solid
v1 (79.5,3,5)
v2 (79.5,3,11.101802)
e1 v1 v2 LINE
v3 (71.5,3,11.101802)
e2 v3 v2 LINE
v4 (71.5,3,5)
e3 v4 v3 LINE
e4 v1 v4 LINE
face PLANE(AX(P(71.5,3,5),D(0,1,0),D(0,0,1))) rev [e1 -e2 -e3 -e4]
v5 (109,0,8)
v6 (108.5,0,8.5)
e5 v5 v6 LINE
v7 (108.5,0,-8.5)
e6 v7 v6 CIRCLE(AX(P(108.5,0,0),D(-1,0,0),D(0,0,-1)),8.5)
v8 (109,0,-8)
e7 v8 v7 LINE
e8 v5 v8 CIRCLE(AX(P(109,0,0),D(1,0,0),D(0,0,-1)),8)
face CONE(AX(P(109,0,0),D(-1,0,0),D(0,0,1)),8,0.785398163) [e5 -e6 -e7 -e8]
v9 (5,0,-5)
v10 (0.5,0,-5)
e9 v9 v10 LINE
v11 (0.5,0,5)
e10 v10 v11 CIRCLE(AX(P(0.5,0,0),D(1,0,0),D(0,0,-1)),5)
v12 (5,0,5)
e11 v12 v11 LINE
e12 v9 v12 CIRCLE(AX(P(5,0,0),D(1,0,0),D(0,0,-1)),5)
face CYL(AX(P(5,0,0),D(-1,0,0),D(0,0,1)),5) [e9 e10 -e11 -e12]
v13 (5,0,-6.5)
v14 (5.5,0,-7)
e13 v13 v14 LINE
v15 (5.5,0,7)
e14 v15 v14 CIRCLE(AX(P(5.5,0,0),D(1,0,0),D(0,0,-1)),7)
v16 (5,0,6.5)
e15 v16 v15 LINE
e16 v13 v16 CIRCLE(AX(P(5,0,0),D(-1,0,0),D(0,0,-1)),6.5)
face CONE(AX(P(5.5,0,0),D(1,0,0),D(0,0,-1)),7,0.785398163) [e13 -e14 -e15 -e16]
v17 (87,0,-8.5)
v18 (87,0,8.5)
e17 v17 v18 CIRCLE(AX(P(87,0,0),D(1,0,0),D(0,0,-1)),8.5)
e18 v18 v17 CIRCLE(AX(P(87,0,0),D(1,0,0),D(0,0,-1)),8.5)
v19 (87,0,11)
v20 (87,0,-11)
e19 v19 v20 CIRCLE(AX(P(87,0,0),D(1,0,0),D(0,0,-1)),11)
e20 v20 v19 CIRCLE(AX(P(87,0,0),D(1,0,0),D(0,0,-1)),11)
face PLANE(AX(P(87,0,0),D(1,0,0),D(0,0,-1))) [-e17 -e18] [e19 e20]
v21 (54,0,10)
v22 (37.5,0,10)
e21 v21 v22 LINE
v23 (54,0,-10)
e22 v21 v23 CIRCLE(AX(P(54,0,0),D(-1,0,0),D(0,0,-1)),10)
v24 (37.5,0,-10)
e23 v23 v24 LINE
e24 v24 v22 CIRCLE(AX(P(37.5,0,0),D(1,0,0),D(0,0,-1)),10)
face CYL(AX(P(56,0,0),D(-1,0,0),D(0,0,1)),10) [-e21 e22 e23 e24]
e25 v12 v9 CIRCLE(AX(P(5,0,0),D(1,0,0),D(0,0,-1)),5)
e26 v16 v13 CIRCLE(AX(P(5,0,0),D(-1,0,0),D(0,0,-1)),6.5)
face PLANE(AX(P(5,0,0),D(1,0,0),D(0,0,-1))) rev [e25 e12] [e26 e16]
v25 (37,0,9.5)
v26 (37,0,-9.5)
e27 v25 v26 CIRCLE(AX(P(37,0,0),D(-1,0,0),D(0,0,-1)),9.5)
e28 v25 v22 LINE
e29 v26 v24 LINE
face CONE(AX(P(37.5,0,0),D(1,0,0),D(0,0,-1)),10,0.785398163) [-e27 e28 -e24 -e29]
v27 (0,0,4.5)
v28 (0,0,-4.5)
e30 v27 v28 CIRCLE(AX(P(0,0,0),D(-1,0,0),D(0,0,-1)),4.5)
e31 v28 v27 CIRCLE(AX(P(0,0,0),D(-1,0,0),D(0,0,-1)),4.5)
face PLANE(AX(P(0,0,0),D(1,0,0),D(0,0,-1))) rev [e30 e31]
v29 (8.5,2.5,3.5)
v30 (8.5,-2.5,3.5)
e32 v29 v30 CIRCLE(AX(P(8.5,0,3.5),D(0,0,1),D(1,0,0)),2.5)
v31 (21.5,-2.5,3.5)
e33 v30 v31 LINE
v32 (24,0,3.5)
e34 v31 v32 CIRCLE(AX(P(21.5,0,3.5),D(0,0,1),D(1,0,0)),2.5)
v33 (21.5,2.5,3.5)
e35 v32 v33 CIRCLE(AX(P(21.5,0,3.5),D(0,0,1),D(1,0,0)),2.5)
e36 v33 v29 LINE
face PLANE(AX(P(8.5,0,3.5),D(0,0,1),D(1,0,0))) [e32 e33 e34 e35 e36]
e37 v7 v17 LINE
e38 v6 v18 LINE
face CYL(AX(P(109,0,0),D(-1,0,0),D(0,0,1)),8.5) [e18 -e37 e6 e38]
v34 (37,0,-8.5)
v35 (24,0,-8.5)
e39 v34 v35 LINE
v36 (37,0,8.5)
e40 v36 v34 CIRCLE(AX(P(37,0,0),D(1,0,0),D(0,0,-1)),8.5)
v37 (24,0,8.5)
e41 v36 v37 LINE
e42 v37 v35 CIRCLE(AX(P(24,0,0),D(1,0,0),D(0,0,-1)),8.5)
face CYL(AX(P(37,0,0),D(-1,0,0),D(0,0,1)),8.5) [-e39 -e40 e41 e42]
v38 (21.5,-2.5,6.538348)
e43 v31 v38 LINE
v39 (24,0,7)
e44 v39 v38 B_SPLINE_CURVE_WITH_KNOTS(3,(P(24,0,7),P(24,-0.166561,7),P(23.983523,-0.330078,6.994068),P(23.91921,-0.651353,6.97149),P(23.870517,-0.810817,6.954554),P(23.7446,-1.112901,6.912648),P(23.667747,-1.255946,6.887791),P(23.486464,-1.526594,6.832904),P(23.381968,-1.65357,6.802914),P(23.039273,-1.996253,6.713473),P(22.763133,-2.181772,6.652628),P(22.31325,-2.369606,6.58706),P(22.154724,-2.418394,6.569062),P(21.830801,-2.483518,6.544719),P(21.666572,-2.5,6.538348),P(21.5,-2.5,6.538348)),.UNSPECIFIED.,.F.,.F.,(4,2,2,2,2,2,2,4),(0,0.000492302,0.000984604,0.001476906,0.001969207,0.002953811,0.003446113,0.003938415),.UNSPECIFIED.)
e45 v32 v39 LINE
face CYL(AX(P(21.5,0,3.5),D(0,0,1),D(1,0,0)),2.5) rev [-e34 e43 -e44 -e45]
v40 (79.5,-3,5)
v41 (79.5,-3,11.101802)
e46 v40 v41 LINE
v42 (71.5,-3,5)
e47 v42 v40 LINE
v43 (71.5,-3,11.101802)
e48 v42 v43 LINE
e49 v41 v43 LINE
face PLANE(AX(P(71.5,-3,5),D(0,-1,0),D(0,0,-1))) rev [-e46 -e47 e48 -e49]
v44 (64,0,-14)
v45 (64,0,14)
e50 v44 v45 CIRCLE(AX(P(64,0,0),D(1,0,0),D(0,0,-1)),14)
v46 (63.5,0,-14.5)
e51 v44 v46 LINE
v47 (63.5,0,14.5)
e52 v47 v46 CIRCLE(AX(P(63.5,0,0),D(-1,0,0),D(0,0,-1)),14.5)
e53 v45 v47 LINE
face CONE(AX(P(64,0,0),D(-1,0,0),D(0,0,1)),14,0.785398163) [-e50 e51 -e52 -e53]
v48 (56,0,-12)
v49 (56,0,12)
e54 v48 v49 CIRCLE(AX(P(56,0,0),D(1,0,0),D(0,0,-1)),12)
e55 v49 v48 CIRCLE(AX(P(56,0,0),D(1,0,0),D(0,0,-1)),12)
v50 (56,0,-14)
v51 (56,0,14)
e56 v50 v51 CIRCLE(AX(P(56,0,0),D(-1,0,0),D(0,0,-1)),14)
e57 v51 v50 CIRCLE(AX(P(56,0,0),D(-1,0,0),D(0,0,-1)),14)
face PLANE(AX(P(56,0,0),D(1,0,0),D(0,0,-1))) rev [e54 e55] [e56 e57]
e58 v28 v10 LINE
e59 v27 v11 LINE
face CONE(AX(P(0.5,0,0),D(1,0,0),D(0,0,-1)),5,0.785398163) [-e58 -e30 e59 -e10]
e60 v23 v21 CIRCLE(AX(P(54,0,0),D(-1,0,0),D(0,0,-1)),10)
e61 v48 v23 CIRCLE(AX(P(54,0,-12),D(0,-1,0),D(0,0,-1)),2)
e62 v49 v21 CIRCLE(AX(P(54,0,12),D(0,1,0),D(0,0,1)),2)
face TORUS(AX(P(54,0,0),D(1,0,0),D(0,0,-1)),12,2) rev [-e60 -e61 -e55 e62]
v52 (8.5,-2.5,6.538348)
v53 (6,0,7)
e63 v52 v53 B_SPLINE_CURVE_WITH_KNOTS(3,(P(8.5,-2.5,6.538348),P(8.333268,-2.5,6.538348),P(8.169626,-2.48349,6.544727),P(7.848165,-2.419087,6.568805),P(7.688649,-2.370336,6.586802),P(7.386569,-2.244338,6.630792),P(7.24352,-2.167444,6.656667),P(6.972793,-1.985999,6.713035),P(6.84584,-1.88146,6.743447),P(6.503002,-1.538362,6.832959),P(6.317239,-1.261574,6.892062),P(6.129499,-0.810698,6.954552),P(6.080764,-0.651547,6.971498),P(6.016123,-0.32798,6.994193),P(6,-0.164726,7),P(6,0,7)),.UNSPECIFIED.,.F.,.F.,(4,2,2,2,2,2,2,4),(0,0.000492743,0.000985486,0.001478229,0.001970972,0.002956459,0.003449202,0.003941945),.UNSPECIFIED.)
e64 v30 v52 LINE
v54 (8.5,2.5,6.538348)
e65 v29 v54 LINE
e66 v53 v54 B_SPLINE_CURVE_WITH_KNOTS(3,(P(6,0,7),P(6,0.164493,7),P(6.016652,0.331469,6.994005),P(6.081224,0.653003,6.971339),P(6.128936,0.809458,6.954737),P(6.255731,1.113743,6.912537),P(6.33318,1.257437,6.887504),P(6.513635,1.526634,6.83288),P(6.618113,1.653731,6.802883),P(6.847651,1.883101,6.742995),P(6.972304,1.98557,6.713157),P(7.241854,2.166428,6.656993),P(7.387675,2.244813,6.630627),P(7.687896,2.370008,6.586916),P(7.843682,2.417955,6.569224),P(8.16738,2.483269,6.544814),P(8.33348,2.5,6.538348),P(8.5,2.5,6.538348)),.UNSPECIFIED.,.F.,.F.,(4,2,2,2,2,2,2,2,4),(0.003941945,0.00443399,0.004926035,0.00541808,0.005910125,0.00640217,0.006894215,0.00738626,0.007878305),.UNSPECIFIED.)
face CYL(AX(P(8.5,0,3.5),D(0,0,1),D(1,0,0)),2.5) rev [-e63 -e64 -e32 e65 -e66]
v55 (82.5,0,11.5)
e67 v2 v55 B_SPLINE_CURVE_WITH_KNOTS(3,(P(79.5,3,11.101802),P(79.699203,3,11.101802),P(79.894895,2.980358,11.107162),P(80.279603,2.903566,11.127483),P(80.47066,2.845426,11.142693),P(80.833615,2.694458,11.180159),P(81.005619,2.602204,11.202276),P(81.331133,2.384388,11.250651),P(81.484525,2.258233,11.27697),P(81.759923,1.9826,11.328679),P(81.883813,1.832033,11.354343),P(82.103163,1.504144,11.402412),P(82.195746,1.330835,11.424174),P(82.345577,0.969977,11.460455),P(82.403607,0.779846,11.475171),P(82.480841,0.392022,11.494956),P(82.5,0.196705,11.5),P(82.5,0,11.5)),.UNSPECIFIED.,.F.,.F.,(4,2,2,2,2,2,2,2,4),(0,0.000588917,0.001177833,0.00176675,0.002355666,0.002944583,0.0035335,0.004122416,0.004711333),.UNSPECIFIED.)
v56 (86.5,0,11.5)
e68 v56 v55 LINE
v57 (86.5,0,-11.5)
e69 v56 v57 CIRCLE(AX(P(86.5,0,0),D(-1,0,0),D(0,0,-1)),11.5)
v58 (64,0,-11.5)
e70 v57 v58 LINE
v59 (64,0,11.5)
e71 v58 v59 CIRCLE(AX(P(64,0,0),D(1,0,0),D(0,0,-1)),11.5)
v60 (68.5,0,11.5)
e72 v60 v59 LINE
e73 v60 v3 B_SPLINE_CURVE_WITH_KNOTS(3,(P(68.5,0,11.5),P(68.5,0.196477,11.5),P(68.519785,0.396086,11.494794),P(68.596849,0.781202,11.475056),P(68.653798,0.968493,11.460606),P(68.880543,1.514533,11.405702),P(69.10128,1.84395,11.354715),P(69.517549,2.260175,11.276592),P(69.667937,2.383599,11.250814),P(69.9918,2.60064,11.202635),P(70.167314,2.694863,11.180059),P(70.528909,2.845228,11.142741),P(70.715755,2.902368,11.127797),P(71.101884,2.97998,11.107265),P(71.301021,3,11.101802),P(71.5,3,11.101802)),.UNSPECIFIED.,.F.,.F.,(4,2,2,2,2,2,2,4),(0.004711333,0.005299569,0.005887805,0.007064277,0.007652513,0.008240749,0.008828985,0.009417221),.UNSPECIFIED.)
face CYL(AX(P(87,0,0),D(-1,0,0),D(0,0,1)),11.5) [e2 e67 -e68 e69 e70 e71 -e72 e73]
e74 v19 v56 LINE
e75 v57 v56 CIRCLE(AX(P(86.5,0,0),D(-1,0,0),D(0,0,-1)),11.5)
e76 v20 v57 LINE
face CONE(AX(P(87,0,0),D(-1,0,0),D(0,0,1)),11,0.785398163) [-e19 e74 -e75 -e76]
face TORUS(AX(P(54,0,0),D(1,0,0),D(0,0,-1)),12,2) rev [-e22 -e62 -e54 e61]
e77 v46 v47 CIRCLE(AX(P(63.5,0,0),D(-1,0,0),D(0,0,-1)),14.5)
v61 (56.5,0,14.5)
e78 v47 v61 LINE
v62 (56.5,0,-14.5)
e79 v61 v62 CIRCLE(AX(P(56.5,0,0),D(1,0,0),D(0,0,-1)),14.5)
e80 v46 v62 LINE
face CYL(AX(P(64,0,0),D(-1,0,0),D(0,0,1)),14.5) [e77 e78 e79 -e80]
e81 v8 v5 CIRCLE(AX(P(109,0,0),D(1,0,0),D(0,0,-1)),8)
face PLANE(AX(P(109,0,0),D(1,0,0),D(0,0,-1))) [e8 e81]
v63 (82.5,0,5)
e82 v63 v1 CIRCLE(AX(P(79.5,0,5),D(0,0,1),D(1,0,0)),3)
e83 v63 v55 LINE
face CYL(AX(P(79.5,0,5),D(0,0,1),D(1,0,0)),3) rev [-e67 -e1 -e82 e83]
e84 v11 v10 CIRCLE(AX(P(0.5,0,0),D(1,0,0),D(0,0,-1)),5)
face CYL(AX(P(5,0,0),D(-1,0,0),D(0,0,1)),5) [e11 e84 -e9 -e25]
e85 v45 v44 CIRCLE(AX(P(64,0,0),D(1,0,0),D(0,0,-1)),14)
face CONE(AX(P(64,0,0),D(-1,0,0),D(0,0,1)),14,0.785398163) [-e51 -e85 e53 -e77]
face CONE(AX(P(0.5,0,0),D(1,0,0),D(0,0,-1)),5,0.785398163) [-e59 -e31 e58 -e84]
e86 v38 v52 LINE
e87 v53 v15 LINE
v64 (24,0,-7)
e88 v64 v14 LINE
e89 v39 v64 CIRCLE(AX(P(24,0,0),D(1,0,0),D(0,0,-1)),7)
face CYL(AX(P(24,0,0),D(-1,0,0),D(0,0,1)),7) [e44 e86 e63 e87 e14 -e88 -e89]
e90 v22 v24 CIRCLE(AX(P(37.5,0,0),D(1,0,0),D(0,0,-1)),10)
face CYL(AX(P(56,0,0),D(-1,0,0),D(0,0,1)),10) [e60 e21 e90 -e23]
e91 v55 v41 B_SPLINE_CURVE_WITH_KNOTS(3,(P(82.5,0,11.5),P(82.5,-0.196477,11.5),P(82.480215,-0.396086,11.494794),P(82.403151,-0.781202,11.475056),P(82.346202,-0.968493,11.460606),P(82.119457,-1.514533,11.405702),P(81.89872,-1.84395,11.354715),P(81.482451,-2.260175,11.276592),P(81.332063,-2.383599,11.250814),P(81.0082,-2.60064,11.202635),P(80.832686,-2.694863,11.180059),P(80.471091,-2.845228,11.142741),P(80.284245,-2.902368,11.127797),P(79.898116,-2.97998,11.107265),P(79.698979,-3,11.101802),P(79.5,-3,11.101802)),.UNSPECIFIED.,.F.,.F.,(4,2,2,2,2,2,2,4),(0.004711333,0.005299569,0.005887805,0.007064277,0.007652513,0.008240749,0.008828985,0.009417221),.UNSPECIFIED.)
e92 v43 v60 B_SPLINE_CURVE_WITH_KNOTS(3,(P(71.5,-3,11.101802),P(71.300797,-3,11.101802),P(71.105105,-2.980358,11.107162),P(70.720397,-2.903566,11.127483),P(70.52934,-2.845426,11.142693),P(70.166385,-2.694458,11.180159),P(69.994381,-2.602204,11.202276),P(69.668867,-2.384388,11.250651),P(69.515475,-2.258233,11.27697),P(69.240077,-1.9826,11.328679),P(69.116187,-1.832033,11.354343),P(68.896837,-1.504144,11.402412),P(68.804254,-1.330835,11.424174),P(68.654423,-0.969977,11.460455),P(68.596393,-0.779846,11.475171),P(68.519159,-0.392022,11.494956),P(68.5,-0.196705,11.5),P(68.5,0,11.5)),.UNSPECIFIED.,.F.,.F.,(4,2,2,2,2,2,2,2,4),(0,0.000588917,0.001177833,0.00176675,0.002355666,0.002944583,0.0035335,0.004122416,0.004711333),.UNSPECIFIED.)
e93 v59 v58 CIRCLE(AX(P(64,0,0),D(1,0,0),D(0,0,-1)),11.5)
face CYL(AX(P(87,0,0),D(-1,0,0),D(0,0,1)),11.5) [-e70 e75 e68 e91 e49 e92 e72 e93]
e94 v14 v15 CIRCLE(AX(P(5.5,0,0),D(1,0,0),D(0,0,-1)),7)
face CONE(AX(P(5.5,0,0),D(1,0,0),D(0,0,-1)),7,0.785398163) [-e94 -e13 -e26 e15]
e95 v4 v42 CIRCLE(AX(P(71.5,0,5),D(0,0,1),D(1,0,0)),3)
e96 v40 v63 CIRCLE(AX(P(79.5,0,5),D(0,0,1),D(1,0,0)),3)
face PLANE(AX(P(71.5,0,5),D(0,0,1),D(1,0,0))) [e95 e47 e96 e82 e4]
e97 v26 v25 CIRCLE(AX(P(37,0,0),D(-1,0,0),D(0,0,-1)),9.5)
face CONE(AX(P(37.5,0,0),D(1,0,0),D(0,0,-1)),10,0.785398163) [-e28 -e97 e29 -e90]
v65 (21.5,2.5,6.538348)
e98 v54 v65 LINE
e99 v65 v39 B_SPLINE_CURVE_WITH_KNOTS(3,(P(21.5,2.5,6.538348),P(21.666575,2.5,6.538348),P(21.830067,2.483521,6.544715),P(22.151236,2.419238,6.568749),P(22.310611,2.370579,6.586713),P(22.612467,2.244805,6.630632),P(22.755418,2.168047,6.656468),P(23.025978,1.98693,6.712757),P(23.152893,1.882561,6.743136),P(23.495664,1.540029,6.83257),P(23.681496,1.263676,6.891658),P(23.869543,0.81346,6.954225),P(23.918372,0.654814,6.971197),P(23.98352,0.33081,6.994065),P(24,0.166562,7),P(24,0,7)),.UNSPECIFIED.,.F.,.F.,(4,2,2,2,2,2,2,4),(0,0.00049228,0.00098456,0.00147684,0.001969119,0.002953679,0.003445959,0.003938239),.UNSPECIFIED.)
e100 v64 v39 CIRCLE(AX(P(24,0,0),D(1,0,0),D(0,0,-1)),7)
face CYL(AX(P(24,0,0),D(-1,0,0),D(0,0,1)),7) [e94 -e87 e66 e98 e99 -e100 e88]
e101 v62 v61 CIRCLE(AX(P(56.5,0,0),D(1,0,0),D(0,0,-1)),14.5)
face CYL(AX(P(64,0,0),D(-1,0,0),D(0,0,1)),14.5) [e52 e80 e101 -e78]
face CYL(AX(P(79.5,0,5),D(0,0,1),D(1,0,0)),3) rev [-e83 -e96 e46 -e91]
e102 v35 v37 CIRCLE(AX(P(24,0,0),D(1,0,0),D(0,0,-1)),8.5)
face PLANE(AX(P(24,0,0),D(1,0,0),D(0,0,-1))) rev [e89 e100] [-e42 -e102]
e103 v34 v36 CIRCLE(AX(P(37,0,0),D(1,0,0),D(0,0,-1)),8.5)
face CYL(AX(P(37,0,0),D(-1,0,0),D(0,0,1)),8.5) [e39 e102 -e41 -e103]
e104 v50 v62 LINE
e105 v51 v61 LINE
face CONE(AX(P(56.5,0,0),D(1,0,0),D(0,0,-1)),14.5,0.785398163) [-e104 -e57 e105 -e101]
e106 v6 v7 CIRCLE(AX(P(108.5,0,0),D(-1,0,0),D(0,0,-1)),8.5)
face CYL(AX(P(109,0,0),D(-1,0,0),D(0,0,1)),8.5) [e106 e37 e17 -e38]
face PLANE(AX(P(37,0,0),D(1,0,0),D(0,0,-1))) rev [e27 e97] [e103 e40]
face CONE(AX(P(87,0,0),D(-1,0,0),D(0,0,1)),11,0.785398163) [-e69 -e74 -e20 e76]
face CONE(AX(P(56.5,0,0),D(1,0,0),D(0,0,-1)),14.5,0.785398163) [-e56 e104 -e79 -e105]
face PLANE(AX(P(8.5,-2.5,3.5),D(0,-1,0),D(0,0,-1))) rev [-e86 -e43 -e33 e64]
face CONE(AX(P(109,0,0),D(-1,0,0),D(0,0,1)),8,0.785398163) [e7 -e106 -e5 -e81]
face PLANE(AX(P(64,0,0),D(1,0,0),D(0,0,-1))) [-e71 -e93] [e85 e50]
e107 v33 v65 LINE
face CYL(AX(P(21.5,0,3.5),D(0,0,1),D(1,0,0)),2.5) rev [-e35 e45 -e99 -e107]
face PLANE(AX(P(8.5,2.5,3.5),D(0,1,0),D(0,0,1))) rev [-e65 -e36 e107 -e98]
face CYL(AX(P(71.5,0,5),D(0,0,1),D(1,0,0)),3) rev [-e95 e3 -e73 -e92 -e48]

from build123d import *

# Parameters (mm, degrees)
SKETCH1_R           = 5
BOSS_EXTRUDE1_DEPTH = 5
SKETCH2_R           = 7
BOSS_EXTRUDE2_DEPTH = 19
SKETCH3_R           = 8.5
BOSS_EXTRUDE3_DEPTH = 13
SKETCH4_R           = 10
BOSS_EXTRUDE4_DEPTH = 19
SKETCH5_R           = 14.5
BOSS_EXTRUDE5_DEPTH = 8
SKETCH6_R           = 11.5
BOSS_EXTRUDE6_DEPTH = 23
SKETCH7_R           = 8.5
BOSS_EXTRUDE7_DEPTH = 22
CHAMFER1_SIZE       = 0.5
CUT_EXTRUDE2_START  = 7
CUT_EXTRUDE2_DEPTH  = 3.5
CUT_EXTRUDE3_START  = 11.5
CUT_EXTRUDE3_DEPTH  = 6.5
FILLET1_R           = 2


with BuildPart() as part:
    # Sketch1 → Boss-Extrude1 (new body)
    with BuildSketch(Plane(origin=(0, 0, 0), x_dir=(0, 0, -1), z_dir=(1, 0, 0))):
        Circle(SKETCH1_R)
    extrude(amount=BOSS_EXTRUDE1_DEPTH)

    # Sketch2 → Boss-Extrude2 (add)
    with BuildSketch(Plane(origin=(5, 0, 0), x_dir=(0, 0, -1), z_dir=(1, 0, 0))):
        Circle(SKETCH2_R)
    extrude(amount=BOSS_EXTRUDE2_DEPTH)

    # Sketch3 → Boss-Extrude3 (add)
    with BuildSketch(Plane(origin=(24, 0, 0), x_dir=(0, 0, -1), z_dir=(1, 0, 0))):
        with Locations(Location((0, 0, 0), (0, 0, 180))):
            Circle(SKETCH3_R)
    extrude(amount=BOSS_EXTRUDE3_DEPTH)

    # Sketch4 → Boss-Extrude4 (add)
    with BuildSketch(Plane(origin=(37, 0, 0), x_dir=(0, 0, -1), z_dir=(1, 0, 0))):
        Circle(SKETCH4_R)
    extrude(amount=BOSS_EXTRUDE4_DEPTH)

    # Sketch5 → Boss-Extrude5 (add)
    with BuildSketch(Plane(origin=(56, 0, 0), x_dir=(0, 0, -1), z_dir=(1, 0, 0))):
        Circle(SKETCH5_R)
    extrude(amount=BOSS_EXTRUDE5_DEPTH)

    # Sketch6 → Boss-Extrude6 (add)
    with BuildSketch(Plane(origin=(64, 0, 0), x_dir=(0, 0, -1), z_dir=(1, 0, 0))):
        Circle(SKETCH6_R)
    extrude(amount=BOSS_EXTRUDE6_DEPTH)

    # Sketch7 → Boss-Extrude7 (add)
    with BuildSketch(Plane(origin=(87, 0, 0), x_dir=(0, 0, -1), z_dir=(1, 0, 0))):
        with Locations(Location((0, 0, 0), (0, 0, 180))):
            Circle(SKETCH7_R)
    extrude(amount=BOSS_EXTRUDE7_DEPTH)

    # Chamfer1
    chamfer1_edges = [part.edges().sort_by_distance(p)[0] for p in [
        (37, 0, 10),
        (56, 0, 14.5),
        (0, 0, 5),
        (64, 0, 14.5),
        (87, 0, 11.5),
        (109, 0, -8.5),
        (5, 0, 7),
    ]]
    chamfer(chamfer1_edges, length=CHAMFER1_SIZE)

    # Sketch8 → Cut-Extrude2 (cut)
    with BuildSketch(Plane.XY.offset(CUT_EXTRUDE2_START)):
        with BuildLine():
            Line((8.5, 2.5), (21.5, 2.5))
            ThreePointArc((21.5, 2.5), (24, 0), (21.5, -2.5))
            Line((21.5, -2.5), (8.5, -2.5))
            ThreePointArc((8.5, -2.5), (6, 0), (8.5, 2.5))
        make_face()
    extrude(amount=-CUT_EXTRUDE2_DEPTH, mode=Mode.SUBTRACT)

    # Sketch9 → Cut-Extrude3 (cut)
    with BuildSketch(Plane.XY.offset(CUT_EXTRUDE3_START)):
        with BuildLine():
            Line((71.5, 3), (79.5, 3))
            ThreePointArc((79.5, 3), (82.5, 0), (79.5, -3))
            Line((79.5, -3), (71.5, -3))
            ThreePointArc((71.5, -3), (68.5, 0), (71.5, 3))
        make_face()
    extrude(amount=-CUT_EXTRUDE3_DEPTH, mode=Mode.SUBTRACT)

    # Fillet1
    fillet1_edges = [part.edges().sort_by_distance(p)[0] for p in [
        (56, 0, 10),
    ]]
    fillet(fillet1_edges, radius=FILLET1_R)


solid = part.part
